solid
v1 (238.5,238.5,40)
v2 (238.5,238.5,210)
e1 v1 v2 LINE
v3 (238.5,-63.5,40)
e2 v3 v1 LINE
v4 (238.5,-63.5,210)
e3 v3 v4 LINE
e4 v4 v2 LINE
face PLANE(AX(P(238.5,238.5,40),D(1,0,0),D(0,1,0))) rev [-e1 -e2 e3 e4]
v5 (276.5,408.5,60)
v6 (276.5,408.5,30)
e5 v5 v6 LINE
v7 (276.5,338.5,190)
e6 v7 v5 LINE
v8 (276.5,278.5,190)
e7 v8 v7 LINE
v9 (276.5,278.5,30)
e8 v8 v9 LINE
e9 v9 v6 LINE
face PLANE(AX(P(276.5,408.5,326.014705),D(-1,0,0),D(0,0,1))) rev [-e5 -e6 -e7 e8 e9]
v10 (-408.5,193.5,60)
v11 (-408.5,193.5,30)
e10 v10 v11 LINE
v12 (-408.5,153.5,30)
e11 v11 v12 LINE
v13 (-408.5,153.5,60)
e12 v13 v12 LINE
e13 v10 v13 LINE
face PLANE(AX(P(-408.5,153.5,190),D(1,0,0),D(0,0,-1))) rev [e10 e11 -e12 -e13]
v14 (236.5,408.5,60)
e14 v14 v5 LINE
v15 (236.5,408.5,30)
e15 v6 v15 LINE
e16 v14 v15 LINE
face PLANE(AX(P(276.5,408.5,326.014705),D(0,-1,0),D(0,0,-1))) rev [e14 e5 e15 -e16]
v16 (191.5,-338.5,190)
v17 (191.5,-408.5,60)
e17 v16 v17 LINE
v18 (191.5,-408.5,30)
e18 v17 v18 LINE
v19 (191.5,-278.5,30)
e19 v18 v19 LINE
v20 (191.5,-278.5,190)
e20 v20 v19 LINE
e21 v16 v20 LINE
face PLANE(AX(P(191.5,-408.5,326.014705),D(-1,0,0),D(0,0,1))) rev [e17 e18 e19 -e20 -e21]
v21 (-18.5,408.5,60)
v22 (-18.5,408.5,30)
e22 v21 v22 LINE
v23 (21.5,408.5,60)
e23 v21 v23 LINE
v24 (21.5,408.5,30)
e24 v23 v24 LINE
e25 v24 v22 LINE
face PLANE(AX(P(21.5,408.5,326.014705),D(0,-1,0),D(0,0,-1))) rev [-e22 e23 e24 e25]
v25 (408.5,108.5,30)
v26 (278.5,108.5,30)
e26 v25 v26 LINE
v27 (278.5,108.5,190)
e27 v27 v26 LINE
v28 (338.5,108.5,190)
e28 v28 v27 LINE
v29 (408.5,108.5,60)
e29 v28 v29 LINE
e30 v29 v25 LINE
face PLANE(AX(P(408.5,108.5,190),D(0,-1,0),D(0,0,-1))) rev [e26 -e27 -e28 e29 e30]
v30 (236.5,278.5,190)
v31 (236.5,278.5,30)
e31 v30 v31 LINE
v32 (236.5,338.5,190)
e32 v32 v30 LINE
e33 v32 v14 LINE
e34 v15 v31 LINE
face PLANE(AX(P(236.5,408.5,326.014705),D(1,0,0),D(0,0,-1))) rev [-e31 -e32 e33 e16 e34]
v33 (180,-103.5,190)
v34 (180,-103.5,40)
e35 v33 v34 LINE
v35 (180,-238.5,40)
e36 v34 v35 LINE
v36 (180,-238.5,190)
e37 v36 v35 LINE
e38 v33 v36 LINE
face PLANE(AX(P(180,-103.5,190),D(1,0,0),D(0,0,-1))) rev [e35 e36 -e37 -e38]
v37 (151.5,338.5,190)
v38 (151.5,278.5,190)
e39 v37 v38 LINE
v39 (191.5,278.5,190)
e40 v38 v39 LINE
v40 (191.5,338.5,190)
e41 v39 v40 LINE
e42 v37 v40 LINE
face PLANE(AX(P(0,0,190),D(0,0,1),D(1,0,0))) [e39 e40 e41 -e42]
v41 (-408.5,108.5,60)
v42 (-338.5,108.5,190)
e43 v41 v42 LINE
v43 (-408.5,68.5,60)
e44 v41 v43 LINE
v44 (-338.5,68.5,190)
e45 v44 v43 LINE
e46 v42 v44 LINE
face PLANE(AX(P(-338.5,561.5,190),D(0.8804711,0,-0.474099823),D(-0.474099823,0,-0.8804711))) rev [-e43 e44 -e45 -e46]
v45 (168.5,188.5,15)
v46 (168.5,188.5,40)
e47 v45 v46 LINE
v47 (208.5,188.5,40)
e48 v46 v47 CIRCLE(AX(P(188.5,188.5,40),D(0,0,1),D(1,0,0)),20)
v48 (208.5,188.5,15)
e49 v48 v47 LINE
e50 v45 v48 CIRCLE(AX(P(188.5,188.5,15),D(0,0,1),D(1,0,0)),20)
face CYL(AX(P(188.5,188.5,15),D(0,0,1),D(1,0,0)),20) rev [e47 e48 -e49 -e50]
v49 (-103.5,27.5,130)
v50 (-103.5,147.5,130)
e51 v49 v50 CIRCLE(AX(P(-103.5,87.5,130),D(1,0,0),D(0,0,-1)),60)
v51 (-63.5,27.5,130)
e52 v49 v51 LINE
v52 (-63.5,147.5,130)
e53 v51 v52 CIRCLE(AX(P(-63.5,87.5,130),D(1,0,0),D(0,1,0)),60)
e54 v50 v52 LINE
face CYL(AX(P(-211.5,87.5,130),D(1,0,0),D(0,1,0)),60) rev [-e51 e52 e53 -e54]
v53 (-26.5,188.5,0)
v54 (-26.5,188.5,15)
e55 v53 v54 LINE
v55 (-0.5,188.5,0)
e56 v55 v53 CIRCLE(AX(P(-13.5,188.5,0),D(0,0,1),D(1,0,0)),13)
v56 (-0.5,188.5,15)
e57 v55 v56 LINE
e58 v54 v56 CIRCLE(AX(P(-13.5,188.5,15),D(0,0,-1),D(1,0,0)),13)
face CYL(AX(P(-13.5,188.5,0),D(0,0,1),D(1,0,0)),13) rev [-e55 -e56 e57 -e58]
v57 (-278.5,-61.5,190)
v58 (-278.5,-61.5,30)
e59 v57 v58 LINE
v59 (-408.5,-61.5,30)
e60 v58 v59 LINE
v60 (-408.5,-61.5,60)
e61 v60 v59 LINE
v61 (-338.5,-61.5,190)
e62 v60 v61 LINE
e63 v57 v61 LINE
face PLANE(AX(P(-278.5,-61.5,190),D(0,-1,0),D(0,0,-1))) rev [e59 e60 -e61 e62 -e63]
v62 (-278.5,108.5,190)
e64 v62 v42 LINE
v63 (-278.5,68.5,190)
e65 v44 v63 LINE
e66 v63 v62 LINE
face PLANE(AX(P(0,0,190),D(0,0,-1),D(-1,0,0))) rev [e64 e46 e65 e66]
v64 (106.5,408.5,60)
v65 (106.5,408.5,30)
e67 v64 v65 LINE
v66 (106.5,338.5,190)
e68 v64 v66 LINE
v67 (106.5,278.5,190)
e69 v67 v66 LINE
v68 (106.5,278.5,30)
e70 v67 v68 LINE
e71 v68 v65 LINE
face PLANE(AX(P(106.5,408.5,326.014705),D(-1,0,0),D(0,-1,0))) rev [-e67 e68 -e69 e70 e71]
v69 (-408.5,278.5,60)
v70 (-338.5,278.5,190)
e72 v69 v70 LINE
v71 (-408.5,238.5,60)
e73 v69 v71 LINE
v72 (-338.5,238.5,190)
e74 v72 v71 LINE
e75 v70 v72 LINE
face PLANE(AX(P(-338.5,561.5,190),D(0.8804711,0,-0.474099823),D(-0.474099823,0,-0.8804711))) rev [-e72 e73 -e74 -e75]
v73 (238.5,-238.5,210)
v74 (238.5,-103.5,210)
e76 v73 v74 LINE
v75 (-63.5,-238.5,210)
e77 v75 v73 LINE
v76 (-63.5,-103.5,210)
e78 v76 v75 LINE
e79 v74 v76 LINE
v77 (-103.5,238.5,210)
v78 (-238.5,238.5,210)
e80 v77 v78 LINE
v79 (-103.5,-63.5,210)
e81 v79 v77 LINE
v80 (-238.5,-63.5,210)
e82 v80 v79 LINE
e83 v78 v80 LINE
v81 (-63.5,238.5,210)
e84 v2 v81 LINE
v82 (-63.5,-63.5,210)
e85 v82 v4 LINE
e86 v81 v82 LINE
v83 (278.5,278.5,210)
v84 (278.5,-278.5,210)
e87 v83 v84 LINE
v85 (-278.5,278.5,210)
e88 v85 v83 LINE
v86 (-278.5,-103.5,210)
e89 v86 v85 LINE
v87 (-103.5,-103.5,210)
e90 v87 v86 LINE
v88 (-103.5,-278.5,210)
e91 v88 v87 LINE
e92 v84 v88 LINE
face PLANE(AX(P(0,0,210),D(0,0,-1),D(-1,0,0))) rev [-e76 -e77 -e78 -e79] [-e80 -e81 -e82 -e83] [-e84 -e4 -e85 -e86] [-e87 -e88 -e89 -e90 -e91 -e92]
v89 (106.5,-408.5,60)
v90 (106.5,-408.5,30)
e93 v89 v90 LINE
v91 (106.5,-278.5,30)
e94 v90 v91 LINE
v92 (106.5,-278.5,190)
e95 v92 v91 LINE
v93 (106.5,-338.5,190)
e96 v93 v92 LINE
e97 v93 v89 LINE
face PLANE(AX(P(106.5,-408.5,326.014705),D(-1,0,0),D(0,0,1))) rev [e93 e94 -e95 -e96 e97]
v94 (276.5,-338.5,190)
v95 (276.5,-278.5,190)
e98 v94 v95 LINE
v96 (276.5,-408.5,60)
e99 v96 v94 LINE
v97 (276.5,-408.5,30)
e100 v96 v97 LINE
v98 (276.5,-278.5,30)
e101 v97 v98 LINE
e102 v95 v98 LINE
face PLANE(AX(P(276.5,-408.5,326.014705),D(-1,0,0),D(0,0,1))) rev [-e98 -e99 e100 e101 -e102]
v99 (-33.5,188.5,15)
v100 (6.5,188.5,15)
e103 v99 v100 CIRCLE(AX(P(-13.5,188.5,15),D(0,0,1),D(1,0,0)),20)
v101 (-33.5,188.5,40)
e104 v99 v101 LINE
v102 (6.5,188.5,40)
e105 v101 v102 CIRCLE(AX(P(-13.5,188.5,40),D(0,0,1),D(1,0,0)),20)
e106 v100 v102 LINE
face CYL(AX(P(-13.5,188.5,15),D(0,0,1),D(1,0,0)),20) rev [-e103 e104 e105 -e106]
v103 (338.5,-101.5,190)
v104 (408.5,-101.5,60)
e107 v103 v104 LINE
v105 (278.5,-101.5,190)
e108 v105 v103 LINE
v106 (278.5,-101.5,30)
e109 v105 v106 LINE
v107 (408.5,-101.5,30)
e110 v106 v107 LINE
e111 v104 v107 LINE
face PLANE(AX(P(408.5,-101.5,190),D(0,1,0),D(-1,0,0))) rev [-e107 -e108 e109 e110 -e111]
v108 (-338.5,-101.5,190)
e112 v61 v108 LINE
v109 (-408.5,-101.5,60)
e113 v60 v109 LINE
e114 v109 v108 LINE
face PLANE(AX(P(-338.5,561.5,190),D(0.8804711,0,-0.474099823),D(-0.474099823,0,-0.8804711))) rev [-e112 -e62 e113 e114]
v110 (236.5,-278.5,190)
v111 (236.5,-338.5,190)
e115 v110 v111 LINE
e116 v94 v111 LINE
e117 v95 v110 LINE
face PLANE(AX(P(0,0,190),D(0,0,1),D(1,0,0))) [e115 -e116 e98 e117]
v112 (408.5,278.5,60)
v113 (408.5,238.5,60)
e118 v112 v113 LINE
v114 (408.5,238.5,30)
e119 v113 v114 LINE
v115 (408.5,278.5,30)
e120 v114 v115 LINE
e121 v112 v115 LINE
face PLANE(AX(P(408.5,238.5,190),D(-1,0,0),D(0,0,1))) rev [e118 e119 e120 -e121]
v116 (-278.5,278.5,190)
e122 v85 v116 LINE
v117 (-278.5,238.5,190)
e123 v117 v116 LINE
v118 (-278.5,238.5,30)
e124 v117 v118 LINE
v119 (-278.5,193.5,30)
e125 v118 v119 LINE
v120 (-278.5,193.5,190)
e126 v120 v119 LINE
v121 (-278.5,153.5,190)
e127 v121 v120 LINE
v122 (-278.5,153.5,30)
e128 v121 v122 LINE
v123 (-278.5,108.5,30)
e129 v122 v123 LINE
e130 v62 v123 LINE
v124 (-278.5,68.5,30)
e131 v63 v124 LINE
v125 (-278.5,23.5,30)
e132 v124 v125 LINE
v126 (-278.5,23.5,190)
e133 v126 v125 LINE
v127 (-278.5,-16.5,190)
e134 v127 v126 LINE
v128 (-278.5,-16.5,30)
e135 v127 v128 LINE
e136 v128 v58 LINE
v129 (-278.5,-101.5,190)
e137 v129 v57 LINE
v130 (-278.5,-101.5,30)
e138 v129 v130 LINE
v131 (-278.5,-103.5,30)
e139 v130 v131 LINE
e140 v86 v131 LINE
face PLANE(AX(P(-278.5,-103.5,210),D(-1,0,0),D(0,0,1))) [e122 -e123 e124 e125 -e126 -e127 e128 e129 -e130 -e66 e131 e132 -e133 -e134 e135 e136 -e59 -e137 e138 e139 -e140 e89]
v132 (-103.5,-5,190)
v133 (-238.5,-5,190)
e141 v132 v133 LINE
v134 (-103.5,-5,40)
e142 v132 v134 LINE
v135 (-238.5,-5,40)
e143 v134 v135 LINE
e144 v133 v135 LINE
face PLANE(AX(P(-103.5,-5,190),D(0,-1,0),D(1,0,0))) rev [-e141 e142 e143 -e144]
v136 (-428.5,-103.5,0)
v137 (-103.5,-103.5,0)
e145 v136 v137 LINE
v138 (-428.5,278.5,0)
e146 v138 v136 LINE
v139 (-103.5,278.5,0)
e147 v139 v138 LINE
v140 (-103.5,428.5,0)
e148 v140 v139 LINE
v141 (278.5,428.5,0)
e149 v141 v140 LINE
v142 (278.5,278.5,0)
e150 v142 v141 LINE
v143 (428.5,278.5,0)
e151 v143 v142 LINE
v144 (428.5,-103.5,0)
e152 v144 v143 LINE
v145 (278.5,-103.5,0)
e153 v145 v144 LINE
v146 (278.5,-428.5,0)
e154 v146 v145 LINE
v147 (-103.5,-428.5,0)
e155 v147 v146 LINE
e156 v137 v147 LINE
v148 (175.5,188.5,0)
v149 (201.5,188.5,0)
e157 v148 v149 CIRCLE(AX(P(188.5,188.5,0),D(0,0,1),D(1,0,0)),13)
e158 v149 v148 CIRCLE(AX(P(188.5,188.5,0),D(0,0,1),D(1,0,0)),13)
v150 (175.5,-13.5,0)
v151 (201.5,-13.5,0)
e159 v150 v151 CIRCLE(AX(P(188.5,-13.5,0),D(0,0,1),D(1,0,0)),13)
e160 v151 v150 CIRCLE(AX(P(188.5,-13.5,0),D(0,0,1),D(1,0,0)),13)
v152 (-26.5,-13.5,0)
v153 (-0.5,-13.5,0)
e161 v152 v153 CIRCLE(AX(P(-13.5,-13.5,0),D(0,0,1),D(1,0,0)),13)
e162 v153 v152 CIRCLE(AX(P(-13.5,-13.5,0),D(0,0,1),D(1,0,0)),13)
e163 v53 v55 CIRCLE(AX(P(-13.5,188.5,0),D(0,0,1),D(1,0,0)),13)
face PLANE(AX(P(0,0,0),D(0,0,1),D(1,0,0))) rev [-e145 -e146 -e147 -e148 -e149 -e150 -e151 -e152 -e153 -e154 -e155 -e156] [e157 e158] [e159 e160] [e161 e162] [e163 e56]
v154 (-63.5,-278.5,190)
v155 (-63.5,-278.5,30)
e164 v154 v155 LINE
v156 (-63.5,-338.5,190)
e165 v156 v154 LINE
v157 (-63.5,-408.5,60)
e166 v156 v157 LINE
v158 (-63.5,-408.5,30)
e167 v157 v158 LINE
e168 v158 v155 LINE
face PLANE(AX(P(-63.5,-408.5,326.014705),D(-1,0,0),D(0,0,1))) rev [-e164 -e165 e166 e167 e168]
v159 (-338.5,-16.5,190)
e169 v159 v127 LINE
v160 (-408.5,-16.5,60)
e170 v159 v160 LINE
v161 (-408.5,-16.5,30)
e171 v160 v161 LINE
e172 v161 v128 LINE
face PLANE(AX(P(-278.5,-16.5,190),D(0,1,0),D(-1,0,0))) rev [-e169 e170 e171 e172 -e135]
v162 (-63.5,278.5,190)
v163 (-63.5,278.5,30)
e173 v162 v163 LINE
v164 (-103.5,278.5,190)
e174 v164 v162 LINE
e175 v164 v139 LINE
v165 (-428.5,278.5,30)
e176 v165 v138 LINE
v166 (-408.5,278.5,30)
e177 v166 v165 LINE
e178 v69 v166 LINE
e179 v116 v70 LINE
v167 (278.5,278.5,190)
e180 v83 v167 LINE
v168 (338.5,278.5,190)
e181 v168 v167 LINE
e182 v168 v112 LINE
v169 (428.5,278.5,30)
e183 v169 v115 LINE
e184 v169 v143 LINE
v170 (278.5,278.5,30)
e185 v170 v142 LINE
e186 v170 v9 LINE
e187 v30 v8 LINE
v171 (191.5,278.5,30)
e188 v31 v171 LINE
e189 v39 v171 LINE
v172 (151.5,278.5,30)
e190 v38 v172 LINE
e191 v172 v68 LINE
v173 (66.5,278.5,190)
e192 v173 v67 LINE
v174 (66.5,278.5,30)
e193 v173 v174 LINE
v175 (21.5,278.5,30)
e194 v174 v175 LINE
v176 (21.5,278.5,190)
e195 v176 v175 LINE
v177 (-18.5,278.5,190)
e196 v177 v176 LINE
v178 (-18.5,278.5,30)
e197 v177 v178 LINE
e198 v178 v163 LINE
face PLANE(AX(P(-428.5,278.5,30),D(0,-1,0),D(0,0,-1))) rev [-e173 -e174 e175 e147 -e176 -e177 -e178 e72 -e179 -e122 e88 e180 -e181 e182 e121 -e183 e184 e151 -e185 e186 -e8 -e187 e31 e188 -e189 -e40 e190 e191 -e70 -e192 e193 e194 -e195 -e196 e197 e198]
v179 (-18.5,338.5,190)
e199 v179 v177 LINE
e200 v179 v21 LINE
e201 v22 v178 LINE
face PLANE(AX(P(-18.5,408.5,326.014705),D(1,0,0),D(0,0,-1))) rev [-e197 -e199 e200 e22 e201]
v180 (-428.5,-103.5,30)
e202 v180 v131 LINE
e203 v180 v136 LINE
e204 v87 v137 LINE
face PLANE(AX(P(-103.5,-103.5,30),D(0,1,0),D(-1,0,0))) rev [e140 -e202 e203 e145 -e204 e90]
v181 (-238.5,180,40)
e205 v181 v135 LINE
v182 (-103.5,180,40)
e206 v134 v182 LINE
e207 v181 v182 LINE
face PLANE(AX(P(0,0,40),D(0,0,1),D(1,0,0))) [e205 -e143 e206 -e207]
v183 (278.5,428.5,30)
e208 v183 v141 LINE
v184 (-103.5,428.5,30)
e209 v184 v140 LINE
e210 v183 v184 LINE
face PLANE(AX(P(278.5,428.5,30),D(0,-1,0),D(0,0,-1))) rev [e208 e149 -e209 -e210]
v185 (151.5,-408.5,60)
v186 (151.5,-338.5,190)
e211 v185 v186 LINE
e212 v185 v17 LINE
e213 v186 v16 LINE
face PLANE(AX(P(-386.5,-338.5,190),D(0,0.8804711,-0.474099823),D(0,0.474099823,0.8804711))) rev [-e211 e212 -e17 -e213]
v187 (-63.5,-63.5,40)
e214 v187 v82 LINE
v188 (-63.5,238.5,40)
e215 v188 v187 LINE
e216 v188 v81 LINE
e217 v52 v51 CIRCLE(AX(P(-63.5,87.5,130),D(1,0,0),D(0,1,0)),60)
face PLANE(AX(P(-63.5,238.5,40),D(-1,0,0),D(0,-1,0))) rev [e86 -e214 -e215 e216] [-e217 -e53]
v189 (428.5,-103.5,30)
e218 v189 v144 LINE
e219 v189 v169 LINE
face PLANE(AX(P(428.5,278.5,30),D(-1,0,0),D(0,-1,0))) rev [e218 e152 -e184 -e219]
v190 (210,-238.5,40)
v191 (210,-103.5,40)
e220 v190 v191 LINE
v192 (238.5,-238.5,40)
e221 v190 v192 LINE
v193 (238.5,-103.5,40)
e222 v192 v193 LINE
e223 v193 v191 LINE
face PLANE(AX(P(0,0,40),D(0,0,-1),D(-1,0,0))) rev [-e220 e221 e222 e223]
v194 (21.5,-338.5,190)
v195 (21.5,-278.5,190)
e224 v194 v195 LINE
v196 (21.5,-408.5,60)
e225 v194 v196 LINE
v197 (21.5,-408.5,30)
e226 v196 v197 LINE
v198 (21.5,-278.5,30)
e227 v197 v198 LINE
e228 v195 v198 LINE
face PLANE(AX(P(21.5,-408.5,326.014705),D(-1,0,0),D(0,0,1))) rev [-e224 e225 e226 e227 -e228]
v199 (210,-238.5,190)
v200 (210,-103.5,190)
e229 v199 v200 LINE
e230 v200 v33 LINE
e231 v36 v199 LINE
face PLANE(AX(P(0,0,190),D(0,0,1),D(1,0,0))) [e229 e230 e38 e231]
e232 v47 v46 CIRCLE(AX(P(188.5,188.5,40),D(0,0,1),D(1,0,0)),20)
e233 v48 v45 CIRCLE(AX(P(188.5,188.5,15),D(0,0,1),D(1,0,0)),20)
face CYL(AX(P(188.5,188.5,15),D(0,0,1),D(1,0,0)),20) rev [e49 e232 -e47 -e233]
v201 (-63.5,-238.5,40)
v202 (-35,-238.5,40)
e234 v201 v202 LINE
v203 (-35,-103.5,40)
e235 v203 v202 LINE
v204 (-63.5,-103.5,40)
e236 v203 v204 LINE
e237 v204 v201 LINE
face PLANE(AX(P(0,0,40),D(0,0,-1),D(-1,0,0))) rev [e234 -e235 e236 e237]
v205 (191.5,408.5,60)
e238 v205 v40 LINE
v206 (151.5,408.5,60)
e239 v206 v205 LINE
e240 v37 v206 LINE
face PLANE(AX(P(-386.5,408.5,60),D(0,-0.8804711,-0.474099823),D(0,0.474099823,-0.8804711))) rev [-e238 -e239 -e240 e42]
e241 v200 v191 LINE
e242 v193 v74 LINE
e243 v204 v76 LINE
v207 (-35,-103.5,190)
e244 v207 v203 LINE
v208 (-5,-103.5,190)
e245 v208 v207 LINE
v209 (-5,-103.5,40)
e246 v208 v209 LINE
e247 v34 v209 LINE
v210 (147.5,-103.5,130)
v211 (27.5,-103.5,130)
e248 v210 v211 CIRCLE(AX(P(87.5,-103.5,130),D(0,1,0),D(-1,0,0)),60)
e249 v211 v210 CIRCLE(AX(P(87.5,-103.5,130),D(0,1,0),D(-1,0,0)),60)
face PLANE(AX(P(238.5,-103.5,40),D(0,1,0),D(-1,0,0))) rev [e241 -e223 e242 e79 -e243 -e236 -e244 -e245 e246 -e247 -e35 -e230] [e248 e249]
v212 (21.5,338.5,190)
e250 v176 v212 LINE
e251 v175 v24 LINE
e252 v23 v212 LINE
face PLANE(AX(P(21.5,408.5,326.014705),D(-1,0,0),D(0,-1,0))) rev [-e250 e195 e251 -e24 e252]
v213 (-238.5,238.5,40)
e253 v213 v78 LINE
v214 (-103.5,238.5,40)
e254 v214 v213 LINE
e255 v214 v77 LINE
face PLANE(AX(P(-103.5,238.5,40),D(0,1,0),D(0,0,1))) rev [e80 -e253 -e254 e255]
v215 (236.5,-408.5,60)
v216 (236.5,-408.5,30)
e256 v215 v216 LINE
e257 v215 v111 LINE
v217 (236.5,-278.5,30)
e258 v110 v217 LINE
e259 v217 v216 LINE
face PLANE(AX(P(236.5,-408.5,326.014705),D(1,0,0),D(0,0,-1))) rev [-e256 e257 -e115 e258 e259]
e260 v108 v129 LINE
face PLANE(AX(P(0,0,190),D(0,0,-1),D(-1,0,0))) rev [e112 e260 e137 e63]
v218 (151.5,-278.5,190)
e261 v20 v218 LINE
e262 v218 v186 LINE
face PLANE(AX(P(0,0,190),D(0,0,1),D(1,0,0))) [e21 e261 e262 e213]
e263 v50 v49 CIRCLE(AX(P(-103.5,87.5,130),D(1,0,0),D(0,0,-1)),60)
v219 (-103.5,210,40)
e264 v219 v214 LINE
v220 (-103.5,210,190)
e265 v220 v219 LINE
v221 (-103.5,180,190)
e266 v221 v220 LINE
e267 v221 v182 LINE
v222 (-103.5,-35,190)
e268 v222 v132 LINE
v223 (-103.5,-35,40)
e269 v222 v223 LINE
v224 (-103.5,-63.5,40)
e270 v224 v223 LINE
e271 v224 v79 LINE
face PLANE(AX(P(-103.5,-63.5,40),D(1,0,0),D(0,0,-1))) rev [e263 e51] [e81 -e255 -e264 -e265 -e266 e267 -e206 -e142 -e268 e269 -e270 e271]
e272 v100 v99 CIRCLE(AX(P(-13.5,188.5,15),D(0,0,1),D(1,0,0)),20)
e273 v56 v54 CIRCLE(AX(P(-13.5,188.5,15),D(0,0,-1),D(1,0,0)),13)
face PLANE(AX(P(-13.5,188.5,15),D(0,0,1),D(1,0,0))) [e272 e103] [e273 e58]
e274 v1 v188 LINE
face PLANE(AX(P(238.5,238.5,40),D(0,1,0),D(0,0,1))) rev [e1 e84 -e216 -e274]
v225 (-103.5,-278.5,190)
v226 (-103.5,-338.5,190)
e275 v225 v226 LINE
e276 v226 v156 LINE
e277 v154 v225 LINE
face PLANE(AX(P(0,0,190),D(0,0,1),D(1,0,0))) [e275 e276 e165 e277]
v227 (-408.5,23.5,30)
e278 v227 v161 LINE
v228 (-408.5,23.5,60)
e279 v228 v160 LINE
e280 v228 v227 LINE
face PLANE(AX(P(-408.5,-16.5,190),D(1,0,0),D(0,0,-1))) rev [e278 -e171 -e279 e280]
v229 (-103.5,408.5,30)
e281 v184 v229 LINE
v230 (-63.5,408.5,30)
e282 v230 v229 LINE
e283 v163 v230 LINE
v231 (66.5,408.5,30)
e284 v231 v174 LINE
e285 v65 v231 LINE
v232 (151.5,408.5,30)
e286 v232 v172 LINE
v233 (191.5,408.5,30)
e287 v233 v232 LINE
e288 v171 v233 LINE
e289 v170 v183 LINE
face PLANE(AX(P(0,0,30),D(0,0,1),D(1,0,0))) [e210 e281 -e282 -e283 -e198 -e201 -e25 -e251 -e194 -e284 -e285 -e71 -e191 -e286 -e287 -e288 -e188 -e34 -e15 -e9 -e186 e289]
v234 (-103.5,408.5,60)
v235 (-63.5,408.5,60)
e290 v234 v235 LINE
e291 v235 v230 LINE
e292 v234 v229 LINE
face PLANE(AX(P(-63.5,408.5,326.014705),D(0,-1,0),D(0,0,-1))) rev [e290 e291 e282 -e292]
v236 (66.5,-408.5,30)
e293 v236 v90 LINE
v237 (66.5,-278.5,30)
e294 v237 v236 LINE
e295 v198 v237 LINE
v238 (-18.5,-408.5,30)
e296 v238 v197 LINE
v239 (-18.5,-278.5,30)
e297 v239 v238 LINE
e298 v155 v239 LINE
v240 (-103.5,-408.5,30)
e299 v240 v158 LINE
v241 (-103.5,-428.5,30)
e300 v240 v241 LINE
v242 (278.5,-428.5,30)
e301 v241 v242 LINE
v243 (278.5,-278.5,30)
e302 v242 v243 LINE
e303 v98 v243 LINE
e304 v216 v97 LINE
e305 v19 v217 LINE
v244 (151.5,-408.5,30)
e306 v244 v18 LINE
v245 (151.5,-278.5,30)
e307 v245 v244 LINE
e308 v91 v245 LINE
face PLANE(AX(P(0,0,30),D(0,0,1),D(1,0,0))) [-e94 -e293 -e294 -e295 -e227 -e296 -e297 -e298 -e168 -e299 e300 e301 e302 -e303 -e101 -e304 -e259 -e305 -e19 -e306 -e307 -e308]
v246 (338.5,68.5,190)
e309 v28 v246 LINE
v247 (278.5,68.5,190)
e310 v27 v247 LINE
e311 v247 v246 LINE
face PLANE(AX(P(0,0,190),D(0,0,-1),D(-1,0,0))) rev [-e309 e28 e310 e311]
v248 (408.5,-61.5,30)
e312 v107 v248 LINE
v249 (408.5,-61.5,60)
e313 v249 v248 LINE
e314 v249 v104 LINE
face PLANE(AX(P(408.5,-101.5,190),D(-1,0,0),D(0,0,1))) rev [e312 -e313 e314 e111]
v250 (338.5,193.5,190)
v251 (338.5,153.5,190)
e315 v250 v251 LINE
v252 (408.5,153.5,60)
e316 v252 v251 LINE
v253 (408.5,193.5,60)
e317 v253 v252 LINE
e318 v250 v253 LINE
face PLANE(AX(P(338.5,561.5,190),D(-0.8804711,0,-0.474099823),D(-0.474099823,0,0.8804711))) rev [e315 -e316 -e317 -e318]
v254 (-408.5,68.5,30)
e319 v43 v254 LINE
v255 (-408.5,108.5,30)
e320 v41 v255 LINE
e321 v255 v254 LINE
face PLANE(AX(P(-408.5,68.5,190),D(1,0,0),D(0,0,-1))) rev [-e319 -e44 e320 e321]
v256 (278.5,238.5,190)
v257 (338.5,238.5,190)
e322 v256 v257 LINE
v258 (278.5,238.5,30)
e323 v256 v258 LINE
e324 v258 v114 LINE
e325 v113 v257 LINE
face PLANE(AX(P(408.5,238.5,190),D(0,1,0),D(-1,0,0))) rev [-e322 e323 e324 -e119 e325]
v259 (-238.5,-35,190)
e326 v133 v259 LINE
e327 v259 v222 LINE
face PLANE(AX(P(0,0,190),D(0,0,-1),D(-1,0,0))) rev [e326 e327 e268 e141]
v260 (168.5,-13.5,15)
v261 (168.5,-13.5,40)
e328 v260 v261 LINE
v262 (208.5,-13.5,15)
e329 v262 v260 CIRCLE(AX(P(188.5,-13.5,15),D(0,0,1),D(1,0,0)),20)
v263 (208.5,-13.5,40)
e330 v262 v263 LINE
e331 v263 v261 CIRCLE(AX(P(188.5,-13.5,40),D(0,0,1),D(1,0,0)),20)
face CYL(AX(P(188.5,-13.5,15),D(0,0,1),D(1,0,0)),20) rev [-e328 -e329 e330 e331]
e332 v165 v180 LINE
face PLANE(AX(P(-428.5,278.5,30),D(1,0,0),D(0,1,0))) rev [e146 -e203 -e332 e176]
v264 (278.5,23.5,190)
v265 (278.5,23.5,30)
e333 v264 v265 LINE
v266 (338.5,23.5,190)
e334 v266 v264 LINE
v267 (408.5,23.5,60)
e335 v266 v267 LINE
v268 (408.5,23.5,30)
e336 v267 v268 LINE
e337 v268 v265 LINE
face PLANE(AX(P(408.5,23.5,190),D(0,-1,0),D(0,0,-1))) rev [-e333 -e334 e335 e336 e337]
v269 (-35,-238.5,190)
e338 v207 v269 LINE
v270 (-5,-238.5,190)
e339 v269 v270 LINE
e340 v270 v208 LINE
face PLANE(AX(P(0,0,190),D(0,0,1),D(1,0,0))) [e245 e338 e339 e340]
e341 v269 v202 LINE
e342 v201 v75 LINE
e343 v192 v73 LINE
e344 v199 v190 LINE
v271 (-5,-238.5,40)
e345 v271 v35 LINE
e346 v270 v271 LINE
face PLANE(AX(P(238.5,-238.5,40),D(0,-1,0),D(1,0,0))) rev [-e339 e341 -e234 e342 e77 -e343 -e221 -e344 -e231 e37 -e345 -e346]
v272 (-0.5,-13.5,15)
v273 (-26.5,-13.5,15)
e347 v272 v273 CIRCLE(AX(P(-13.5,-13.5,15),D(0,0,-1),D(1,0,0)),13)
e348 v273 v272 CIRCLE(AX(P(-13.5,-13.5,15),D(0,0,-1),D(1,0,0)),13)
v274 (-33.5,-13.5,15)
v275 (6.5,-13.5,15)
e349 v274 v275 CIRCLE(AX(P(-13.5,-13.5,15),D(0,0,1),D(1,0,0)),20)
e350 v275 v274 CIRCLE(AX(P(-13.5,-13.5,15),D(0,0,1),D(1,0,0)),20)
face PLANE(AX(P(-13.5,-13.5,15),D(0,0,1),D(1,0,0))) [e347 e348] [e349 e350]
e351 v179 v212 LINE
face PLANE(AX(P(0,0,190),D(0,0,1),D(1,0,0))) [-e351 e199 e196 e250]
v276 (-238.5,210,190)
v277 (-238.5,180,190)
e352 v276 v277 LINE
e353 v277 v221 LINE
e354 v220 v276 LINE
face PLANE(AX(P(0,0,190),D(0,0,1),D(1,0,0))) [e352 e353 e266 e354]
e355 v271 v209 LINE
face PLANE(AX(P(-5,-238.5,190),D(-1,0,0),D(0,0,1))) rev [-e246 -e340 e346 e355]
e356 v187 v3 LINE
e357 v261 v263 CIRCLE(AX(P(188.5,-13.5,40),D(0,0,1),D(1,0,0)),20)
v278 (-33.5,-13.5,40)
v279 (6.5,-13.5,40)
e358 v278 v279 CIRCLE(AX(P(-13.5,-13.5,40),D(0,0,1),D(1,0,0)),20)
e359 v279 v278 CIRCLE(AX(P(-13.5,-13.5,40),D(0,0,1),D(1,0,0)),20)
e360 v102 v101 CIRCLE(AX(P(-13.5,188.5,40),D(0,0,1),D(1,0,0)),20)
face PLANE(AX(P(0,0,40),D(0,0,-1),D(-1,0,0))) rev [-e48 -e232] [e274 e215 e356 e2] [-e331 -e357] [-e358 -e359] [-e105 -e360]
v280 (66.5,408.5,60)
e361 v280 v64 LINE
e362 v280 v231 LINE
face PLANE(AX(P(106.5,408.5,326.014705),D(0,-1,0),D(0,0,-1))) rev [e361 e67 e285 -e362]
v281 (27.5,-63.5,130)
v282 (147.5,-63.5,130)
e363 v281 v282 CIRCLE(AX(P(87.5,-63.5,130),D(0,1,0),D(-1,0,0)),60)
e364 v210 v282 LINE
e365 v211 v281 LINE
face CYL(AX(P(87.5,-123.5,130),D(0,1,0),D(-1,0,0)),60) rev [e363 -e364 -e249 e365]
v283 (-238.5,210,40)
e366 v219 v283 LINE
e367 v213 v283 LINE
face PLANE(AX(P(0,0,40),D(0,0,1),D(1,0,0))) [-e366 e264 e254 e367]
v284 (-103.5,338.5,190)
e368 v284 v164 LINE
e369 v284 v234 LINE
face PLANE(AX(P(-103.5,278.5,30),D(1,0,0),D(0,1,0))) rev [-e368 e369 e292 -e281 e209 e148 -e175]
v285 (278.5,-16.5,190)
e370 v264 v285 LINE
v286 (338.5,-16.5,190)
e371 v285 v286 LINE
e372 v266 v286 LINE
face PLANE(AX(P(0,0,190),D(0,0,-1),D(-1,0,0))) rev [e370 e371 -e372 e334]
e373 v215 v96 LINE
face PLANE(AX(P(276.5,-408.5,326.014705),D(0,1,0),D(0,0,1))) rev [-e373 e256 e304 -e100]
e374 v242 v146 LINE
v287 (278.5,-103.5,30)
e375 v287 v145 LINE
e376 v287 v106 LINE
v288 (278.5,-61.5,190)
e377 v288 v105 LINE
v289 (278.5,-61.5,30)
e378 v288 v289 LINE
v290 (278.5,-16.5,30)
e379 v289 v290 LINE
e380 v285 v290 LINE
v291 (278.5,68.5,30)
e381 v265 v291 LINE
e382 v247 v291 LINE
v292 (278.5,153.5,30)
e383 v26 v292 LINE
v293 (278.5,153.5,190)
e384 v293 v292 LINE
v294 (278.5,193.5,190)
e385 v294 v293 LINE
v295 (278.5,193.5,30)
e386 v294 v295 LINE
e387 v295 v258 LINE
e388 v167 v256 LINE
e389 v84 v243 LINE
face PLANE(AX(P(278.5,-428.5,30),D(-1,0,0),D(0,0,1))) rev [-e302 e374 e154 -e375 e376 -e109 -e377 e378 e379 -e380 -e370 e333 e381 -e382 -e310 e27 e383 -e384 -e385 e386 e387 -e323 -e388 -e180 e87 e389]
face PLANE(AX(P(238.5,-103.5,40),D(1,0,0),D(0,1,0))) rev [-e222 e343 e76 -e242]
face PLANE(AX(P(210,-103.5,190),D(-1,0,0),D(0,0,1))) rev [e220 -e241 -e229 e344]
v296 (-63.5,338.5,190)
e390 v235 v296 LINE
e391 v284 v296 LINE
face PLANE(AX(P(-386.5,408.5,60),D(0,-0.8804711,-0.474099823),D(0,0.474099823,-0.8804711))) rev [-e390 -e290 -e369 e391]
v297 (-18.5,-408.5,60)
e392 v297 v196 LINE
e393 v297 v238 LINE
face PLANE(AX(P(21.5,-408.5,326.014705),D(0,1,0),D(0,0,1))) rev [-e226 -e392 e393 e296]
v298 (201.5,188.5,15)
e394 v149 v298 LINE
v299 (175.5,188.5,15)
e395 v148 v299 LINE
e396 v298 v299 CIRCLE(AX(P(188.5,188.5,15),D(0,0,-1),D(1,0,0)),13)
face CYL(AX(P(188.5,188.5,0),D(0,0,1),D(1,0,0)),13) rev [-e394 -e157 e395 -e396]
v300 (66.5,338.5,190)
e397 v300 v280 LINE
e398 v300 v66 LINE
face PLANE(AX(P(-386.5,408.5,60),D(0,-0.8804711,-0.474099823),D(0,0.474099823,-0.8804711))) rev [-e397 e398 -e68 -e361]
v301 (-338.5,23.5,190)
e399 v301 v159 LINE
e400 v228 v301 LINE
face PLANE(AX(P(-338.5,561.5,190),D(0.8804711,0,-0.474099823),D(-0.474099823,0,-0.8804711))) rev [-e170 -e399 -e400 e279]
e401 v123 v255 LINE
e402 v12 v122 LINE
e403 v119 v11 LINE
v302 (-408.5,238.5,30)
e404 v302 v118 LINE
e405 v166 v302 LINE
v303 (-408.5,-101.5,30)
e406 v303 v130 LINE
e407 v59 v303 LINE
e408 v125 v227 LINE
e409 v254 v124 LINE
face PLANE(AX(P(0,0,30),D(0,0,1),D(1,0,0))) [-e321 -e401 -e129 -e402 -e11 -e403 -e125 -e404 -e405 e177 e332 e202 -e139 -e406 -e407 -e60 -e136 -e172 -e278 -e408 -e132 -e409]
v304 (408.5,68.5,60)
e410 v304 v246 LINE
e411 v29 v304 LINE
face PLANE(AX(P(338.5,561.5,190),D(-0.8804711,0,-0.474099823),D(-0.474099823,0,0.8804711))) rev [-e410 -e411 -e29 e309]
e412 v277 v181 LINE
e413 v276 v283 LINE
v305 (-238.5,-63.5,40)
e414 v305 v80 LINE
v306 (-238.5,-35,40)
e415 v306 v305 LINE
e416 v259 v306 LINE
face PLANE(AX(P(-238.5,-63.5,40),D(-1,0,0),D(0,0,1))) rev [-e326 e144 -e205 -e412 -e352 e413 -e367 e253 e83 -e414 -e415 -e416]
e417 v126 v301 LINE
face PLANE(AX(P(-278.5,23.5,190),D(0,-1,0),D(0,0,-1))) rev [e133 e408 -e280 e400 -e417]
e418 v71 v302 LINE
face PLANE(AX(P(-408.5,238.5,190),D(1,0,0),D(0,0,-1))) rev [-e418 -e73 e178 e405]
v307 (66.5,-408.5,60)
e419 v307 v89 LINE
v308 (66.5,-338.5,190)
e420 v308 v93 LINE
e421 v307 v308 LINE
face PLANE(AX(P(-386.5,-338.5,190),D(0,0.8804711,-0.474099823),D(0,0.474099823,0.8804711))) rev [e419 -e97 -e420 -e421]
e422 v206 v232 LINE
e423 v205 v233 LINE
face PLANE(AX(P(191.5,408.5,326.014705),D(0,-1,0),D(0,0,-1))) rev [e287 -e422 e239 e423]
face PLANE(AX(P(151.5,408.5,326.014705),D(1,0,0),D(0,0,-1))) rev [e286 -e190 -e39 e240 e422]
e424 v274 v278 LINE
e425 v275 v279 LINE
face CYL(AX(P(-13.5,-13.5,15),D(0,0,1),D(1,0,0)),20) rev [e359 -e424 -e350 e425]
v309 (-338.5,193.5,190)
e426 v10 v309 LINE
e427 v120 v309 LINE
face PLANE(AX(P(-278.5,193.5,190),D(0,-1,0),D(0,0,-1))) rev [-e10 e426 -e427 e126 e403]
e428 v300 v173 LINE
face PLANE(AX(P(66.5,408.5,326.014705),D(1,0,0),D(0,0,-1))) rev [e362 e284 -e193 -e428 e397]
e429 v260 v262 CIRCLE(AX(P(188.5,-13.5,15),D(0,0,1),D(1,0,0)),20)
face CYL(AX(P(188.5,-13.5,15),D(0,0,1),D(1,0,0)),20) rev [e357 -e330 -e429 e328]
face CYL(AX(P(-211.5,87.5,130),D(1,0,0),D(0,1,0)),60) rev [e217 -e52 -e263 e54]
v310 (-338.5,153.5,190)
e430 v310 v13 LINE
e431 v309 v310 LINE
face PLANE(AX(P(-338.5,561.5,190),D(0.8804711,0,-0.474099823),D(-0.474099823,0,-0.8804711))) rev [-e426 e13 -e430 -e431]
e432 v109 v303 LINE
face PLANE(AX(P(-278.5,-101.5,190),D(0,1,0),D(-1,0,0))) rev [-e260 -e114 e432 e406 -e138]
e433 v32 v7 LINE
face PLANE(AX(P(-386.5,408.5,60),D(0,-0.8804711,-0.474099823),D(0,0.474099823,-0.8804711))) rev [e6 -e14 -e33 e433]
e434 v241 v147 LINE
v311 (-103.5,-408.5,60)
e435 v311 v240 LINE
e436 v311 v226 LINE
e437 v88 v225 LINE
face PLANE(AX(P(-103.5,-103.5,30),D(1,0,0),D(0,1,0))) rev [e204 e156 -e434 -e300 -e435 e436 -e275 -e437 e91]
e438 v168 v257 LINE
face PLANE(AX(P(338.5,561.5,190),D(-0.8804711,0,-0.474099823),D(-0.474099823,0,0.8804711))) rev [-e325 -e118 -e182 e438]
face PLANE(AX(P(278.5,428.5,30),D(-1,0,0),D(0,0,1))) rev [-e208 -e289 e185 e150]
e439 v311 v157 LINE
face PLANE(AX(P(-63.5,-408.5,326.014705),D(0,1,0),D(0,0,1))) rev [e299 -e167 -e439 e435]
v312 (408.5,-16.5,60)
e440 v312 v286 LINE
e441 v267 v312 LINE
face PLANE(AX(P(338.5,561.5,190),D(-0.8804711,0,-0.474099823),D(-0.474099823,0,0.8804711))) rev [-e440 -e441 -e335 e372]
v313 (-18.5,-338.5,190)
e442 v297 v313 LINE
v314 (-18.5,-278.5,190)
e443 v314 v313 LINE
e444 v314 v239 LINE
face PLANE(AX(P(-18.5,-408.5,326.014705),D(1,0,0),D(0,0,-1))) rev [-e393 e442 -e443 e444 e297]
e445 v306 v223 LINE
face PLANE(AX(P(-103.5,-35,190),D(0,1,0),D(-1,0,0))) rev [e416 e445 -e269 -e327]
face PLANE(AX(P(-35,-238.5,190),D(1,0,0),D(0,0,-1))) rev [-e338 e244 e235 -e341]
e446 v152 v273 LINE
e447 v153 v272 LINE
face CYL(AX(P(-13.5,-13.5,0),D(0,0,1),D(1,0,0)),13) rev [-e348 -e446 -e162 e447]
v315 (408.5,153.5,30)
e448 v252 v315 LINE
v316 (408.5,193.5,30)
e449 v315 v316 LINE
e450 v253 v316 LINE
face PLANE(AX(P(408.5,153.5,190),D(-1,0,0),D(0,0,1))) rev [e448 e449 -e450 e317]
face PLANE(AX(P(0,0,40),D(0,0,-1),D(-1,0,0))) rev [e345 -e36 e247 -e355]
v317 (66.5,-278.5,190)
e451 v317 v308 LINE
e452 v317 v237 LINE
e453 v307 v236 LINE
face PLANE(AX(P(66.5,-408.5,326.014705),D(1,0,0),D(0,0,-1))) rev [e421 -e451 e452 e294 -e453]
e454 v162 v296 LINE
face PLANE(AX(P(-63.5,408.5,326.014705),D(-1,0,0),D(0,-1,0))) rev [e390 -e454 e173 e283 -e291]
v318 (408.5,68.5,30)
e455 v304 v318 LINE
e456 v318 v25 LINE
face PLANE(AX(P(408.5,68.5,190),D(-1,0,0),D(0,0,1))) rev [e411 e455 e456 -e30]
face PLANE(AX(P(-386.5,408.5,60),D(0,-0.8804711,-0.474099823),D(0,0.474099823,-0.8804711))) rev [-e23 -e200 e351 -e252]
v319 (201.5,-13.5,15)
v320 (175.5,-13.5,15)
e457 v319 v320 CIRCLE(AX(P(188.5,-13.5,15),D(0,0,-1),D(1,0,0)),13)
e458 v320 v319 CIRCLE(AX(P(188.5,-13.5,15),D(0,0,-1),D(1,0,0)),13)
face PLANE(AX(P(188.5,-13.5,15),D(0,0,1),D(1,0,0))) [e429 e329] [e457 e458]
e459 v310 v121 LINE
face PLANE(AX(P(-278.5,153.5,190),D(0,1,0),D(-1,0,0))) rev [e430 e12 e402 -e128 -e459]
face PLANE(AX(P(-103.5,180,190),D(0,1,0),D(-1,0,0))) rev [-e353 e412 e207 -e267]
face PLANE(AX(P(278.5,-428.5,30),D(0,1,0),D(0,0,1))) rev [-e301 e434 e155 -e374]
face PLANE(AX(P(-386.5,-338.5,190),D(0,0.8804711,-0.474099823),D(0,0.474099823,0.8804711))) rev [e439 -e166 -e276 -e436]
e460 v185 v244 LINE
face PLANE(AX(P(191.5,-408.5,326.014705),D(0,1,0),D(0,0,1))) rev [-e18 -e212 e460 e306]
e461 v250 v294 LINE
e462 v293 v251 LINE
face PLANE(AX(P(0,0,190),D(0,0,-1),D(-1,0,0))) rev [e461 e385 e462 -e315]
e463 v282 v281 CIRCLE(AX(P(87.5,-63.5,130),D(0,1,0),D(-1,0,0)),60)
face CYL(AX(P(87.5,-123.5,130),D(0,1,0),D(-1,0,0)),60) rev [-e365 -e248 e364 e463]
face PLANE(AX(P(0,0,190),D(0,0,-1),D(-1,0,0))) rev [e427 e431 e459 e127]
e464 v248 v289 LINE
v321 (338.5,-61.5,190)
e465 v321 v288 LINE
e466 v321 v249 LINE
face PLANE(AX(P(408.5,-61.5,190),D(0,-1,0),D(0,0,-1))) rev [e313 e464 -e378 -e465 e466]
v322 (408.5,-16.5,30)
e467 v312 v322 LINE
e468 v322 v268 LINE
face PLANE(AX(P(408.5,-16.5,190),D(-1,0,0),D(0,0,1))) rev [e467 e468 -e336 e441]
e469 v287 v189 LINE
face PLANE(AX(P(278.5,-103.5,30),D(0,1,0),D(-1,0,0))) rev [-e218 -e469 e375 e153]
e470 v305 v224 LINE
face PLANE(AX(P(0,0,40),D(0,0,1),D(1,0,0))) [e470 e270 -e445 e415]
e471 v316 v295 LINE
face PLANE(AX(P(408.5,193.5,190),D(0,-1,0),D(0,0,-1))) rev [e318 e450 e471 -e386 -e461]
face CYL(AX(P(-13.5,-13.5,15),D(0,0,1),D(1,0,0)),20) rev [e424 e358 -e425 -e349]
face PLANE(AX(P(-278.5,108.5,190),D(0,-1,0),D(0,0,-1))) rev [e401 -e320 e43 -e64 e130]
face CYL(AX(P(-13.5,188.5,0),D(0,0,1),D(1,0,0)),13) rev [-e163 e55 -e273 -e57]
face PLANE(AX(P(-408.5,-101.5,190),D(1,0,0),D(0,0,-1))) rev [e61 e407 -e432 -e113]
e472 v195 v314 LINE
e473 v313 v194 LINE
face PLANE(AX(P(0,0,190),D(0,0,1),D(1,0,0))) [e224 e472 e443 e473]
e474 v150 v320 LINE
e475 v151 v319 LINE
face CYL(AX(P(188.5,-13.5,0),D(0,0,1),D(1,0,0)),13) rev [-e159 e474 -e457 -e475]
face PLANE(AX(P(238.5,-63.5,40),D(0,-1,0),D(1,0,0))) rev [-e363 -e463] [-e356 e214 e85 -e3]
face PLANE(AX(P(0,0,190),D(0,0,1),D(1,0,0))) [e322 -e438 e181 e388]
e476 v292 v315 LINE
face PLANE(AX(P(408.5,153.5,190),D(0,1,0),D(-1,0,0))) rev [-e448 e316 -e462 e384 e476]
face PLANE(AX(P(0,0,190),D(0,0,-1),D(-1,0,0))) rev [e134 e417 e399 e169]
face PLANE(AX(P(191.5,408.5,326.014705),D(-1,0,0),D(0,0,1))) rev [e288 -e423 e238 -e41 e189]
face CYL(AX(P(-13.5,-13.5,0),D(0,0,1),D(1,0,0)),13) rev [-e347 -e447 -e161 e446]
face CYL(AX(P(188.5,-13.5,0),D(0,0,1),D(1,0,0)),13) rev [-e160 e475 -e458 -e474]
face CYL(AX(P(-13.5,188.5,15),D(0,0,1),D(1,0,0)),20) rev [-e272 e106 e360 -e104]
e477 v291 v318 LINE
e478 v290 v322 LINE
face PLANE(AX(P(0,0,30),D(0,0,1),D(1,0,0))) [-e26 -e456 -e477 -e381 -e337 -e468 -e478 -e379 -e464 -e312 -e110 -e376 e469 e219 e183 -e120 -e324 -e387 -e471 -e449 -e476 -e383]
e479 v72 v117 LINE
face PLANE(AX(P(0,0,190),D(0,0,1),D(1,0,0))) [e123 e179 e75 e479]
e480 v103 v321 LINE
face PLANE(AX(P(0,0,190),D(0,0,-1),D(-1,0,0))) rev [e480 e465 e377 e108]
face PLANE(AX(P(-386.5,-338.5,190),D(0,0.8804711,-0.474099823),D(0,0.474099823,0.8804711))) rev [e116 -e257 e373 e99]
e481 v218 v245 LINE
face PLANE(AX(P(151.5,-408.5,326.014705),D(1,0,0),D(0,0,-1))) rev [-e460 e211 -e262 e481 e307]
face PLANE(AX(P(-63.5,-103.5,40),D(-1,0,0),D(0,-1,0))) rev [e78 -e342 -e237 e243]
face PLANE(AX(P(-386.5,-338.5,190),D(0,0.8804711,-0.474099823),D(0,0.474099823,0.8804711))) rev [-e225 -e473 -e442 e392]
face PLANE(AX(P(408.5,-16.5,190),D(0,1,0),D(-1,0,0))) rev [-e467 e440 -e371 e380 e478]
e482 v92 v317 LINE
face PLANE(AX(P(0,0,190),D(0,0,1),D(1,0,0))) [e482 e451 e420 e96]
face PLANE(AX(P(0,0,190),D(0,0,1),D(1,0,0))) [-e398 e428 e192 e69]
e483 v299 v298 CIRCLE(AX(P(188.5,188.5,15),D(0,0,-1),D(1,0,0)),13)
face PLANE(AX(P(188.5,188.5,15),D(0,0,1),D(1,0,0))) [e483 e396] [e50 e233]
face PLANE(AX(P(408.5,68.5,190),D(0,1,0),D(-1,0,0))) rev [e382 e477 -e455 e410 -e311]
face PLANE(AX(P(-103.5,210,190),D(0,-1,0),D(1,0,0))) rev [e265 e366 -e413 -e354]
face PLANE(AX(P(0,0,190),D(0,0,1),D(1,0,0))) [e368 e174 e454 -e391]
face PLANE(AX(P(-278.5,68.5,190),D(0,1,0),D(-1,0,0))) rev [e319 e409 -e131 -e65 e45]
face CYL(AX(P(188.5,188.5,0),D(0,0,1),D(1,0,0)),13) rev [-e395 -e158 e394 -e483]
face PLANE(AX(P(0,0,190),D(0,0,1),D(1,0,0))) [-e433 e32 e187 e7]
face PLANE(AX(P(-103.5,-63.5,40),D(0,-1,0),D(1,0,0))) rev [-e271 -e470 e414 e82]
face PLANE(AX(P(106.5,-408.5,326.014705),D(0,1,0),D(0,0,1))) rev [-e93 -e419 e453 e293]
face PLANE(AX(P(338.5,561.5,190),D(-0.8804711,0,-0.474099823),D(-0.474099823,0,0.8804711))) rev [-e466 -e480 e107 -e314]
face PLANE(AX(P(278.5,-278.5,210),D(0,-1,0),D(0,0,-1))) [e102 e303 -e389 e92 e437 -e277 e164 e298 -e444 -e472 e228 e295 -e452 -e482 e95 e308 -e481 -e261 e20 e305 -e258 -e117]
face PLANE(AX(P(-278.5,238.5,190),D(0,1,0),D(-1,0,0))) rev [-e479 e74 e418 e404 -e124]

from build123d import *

# Parameters (mm, degrees)
BOSS_EXTRUDE1_DEPTH = 30
BOSS_EXTRUDE2_DEPTH = 210
SKETCH6_W           = 302
SKETCH6_H           = 302
SKETCH6_W_2         = 135
SKETCH6_H_2         = 135
CUT_EXTRUDE3_DEPTH  = 170
SKETCH7_R           = 60
CUT_EXTRUDE4_DEPTH  = 148
SKETCH8_W           = 130
SKETCH8_H           = 40
BOSS_EXTRUDE3_DEPTH = 160
SKETCH9_W           = 40
SKETCH9_H           = 130
BOSS_EXTRUDE4_DEPTH = 160
SKETCH10_W          = 135
SKETCH10_H          = 30
SKETCH10_W_2        = 30
SKETCH10_H_2        = 135
BOSS_EXTRUDE5_DEPTH = 150
CUT_EXTRUDE5_DEPTH  = 663
CUT_EXTRUDE6_DEPTH  = 663
SKETCH14_R          = 60
CUT_EXTRUDE7_DEPTH  = 60
SKETCH16_R          = 13
CUT_EXTRUDE10_DEPTH = 40
SKETCH18_R          = 20
CUT_EXTRUDE11_DEPTH = 25


with BuildPart() as part:
    # Sketch1 → Boss-Extrude1 (new body)
    with BuildSketch(Plane.XY):
        Polygon((278.5, -428.5), (278.5, -103.5), (428.5, -103.5), (428.5, 278.5), (278.5, 278.5), (278.5, 428.5), (-103.5, 428.5), (-103.5, 278.5), (-428.5, 278.5), (-428.5, -103.5), (-103.5, -103.5), (-103.5, -428.5), align=None)
    extrude(amount=BOSS_EXTRUDE1_DEPTH)

    # Sketch4 → Boss-Extrude2 (add)
    with BuildSketch(Plane(origin=(0, 0, 0), x_dir=(-1, 0, 0), z_dir=(0, 0, -1))):
        Polygon((-278.5, -278.5), (103.5, -278.5), (103.5, -103.5), (278.5, -103.5), (278.5, 278.5), (103.5, 278.5), (-278.5, 278.5), align=None)
    extrude(amount=-BOSS_EXTRUDE2_DEPTH)

    # Sketch6 → Cut-Extrude3 (cut)
    with BuildSketch(Plane.XY.offset(210)):
        with Locations((87.5, 87.5)):
            Rectangle(SKETCH6_W, SKETCH6_H)
        with Locations((-171, 87.5)):
            Rectangle(SKETCH6_W_2, SKETCH6_H)
        with Locations((87.5, -171)):
            Rectangle(SKETCH6_W, SKETCH6_H_2)
    extrude(amount=-CUT_EXTRUDE3_DEPTH, mode=Mode.SUBTRACT)

    # Sketch7 → Cut-Extrude4 (cut)
    with BuildSketch(Plane(origin=(-63.5, 0, 0), x_dir=(0, 0, -1), z_dir=(1, 0, 0))):
        with Locations(Location((-130, 87.5, 0), (0, 0, 90))):
            Circle(SKETCH7_R)
    extrude(amount=-CUT_EXTRUDE4_DEPTH, mode=Mode.SUBTRACT)

    # Sketch8 → Boss-Extrude3 (add)
    with BuildSketch(Plane.XY.offset(30)):
        with Locations((-343.5, 258.5)):
            Rectangle(SKETCH8_W, SKETCH8_H)
        with Locations((-343.5, 173.5)):
            Rectangle(SKETCH8_W, SKETCH8_H)
        with Locations((-343.5, 88.5)):
            Rectangle(SKETCH8_W, SKETCH8_H)
        with Locations((-343.5, 3.5)):
            Rectangle(SKETCH8_W, SKETCH8_H)
        with Locations((-343.5, -81.5)):
            Rectangle(SKETCH8_W, SKETCH8_H)
        with Locations((343.5, 173.5)):
            Rectangle(SKETCH8_W, SKETCH8_H)
        with Locations((343.5, 258.5)):
            Rectangle(SKETCH8_W, SKETCH8_H)
        with Locations((343.5, 88.5)):
            Rectangle(SKETCH8_W, SKETCH8_H)
        with Locations((343.5, 3.5)):
            Rectangle(SKETCH8_W, SKETCH8_H)
        with Locations((343.5, -81.5)):
            Rectangle(SKETCH8_W, SKETCH8_H)
    extrude(amount=BOSS_EXTRUDE3_DEPTH)

    # Sketch9 → Boss-Extrude4 (add)
    with BuildSketch(Plane.XY.offset(30)):
        with Locations((1.5, -343.5)):
            Rectangle(SKETCH9_W, SKETCH9_H)
        with Locations((-83.5, -343.5)):
            Rectangle(SKETCH9_W, SKETCH9_H)
        with Locations((-83.5, 343.5)):
            Rectangle(SKETCH9_W, SKETCH9_H)
        with Locations((1.5, 343.5)):
            Rectangle(SKETCH9_W, SKETCH9_H)
        with Locations((86.5, -343.5)):
            Rectangle(SKETCH9_W, SKETCH9_H)
        with Locations((86.5, 343.5)):
            Rectangle(SKETCH9_W, SKETCH9_H)
        with Locations((171.5, -343.5)):
            Rectangle(SKETCH9_W, SKETCH9_H)
        with Locations((171.5, 343.5)):
            Rectangle(SKETCH9_W, SKETCH9_H)
        with Locations((256.5, -343.5)):
            Rectangle(SKETCH9_W, SKETCH9_H)
        with Locations((256.5, 343.5)):
            Rectangle(SKETCH9_W, SKETCH9_H)
    extrude(amount=BOSS_EXTRUDE4_DEPTH)

    # Sketch10 → Boss-Extrude5 (add)
    with BuildSketch(Plane.XY.offset(40)):
        with Locations((-171, 195)):
            Rectangle(SKETCH10_W, SKETCH10_H)
        with Locations((-171, -20)):
            Rectangle(SKETCH10_W, SKETCH10_H)
        with Locations((-20, -171)):
            Rectangle(SKETCH10_W_2, SKETCH10_H_2)
        with Locations((195, -171)):
            Rectangle(SKETCH10_W_2, SKETCH10_H_2)
    extrude(amount=BOSS_EXTRUDE5_DEPTH)

    # Sketch11 → Cut-Extrude5 (cut)
    with BuildSketch(Plane.XZ.offset(101.5)):
        Polygon((-338.5, 190), (-408.5, 60), (-408.5, 190), align=None)
        Polygon((338.5, 190), (408.5, 60), (408.5, 190), align=None)
    extrude(amount=-CUT_EXTRUDE5_DEPTH, mode=Mode.SUBTRACT)

    # Sketch12 → Cut-Extrude6 (cut)
    with BuildSketch(Plane(origin=(276.5, 0, 0), x_dir=(0, 0, -1), z_dir=(1, 0, 0))):
        Polygon((-60, 408.5), (-190, 338.5), (-190, 408.5), align=None)
        Polygon((-190, -338.5), (-60, -408.5), (-190, -408.5), align=None)
    extrude(amount=-CUT_EXTRUDE6_DEPTH, mode=Mode.SUBTRACT)

    # Sketch14 → Cut-Extrude7 (cut)
    with BuildSketch(Plane(origin=(0, -63.5, 0), x_dir=(1, 0, 0), z_dir=(0, 1, 0))):
        with Locations(Location((87.5, -130, 0), (0, 0, 180))):
            Circle(SKETCH14_R)
    extrude(amount=-CUT_EXTRUDE7_DEPTH, mode=Mode.SUBTRACT)

    # Sketch16 → Cut-Extrude10 (cut)
    with BuildSketch(Plane.XY.offset(40)):
        with Locations((-13.5, 188.5)):
            Circle(SKETCH16_R)
        with Locations((188.5, 188.5)):
            Circle(SKETCH16_R)
        with Locations((-13.5, -13.5)):
            Circle(SKETCH16_R)
        with Locations((188.5, -13.5)):
            Circle(SKETCH16_R)
    extrude(amount=-CUT_EXTRUDE10_DEPTH, mode=Mode.SUBTRACT)

    # Sketch18 → Cut-Extrude11 (cut)
    with BuildSketch(Plane.XY.offset(40)):
        with Locations((-13.5, 188.5)):
            Circle(SKETCH18_R)
        with Locations((188.5, 188.5)):
            Circle(SKETCH18_R)
        with Locations((-13.5, -13.5)):
            Circle(SKETCH18_R)
        with Locations((188.5, -13.5)):
            Circle(SKETCH18_R)
    extrude(amount=-CUT_EXTRUDE11_DEPTH, mode=Mode.SUBTRACT)


solid = part.part
